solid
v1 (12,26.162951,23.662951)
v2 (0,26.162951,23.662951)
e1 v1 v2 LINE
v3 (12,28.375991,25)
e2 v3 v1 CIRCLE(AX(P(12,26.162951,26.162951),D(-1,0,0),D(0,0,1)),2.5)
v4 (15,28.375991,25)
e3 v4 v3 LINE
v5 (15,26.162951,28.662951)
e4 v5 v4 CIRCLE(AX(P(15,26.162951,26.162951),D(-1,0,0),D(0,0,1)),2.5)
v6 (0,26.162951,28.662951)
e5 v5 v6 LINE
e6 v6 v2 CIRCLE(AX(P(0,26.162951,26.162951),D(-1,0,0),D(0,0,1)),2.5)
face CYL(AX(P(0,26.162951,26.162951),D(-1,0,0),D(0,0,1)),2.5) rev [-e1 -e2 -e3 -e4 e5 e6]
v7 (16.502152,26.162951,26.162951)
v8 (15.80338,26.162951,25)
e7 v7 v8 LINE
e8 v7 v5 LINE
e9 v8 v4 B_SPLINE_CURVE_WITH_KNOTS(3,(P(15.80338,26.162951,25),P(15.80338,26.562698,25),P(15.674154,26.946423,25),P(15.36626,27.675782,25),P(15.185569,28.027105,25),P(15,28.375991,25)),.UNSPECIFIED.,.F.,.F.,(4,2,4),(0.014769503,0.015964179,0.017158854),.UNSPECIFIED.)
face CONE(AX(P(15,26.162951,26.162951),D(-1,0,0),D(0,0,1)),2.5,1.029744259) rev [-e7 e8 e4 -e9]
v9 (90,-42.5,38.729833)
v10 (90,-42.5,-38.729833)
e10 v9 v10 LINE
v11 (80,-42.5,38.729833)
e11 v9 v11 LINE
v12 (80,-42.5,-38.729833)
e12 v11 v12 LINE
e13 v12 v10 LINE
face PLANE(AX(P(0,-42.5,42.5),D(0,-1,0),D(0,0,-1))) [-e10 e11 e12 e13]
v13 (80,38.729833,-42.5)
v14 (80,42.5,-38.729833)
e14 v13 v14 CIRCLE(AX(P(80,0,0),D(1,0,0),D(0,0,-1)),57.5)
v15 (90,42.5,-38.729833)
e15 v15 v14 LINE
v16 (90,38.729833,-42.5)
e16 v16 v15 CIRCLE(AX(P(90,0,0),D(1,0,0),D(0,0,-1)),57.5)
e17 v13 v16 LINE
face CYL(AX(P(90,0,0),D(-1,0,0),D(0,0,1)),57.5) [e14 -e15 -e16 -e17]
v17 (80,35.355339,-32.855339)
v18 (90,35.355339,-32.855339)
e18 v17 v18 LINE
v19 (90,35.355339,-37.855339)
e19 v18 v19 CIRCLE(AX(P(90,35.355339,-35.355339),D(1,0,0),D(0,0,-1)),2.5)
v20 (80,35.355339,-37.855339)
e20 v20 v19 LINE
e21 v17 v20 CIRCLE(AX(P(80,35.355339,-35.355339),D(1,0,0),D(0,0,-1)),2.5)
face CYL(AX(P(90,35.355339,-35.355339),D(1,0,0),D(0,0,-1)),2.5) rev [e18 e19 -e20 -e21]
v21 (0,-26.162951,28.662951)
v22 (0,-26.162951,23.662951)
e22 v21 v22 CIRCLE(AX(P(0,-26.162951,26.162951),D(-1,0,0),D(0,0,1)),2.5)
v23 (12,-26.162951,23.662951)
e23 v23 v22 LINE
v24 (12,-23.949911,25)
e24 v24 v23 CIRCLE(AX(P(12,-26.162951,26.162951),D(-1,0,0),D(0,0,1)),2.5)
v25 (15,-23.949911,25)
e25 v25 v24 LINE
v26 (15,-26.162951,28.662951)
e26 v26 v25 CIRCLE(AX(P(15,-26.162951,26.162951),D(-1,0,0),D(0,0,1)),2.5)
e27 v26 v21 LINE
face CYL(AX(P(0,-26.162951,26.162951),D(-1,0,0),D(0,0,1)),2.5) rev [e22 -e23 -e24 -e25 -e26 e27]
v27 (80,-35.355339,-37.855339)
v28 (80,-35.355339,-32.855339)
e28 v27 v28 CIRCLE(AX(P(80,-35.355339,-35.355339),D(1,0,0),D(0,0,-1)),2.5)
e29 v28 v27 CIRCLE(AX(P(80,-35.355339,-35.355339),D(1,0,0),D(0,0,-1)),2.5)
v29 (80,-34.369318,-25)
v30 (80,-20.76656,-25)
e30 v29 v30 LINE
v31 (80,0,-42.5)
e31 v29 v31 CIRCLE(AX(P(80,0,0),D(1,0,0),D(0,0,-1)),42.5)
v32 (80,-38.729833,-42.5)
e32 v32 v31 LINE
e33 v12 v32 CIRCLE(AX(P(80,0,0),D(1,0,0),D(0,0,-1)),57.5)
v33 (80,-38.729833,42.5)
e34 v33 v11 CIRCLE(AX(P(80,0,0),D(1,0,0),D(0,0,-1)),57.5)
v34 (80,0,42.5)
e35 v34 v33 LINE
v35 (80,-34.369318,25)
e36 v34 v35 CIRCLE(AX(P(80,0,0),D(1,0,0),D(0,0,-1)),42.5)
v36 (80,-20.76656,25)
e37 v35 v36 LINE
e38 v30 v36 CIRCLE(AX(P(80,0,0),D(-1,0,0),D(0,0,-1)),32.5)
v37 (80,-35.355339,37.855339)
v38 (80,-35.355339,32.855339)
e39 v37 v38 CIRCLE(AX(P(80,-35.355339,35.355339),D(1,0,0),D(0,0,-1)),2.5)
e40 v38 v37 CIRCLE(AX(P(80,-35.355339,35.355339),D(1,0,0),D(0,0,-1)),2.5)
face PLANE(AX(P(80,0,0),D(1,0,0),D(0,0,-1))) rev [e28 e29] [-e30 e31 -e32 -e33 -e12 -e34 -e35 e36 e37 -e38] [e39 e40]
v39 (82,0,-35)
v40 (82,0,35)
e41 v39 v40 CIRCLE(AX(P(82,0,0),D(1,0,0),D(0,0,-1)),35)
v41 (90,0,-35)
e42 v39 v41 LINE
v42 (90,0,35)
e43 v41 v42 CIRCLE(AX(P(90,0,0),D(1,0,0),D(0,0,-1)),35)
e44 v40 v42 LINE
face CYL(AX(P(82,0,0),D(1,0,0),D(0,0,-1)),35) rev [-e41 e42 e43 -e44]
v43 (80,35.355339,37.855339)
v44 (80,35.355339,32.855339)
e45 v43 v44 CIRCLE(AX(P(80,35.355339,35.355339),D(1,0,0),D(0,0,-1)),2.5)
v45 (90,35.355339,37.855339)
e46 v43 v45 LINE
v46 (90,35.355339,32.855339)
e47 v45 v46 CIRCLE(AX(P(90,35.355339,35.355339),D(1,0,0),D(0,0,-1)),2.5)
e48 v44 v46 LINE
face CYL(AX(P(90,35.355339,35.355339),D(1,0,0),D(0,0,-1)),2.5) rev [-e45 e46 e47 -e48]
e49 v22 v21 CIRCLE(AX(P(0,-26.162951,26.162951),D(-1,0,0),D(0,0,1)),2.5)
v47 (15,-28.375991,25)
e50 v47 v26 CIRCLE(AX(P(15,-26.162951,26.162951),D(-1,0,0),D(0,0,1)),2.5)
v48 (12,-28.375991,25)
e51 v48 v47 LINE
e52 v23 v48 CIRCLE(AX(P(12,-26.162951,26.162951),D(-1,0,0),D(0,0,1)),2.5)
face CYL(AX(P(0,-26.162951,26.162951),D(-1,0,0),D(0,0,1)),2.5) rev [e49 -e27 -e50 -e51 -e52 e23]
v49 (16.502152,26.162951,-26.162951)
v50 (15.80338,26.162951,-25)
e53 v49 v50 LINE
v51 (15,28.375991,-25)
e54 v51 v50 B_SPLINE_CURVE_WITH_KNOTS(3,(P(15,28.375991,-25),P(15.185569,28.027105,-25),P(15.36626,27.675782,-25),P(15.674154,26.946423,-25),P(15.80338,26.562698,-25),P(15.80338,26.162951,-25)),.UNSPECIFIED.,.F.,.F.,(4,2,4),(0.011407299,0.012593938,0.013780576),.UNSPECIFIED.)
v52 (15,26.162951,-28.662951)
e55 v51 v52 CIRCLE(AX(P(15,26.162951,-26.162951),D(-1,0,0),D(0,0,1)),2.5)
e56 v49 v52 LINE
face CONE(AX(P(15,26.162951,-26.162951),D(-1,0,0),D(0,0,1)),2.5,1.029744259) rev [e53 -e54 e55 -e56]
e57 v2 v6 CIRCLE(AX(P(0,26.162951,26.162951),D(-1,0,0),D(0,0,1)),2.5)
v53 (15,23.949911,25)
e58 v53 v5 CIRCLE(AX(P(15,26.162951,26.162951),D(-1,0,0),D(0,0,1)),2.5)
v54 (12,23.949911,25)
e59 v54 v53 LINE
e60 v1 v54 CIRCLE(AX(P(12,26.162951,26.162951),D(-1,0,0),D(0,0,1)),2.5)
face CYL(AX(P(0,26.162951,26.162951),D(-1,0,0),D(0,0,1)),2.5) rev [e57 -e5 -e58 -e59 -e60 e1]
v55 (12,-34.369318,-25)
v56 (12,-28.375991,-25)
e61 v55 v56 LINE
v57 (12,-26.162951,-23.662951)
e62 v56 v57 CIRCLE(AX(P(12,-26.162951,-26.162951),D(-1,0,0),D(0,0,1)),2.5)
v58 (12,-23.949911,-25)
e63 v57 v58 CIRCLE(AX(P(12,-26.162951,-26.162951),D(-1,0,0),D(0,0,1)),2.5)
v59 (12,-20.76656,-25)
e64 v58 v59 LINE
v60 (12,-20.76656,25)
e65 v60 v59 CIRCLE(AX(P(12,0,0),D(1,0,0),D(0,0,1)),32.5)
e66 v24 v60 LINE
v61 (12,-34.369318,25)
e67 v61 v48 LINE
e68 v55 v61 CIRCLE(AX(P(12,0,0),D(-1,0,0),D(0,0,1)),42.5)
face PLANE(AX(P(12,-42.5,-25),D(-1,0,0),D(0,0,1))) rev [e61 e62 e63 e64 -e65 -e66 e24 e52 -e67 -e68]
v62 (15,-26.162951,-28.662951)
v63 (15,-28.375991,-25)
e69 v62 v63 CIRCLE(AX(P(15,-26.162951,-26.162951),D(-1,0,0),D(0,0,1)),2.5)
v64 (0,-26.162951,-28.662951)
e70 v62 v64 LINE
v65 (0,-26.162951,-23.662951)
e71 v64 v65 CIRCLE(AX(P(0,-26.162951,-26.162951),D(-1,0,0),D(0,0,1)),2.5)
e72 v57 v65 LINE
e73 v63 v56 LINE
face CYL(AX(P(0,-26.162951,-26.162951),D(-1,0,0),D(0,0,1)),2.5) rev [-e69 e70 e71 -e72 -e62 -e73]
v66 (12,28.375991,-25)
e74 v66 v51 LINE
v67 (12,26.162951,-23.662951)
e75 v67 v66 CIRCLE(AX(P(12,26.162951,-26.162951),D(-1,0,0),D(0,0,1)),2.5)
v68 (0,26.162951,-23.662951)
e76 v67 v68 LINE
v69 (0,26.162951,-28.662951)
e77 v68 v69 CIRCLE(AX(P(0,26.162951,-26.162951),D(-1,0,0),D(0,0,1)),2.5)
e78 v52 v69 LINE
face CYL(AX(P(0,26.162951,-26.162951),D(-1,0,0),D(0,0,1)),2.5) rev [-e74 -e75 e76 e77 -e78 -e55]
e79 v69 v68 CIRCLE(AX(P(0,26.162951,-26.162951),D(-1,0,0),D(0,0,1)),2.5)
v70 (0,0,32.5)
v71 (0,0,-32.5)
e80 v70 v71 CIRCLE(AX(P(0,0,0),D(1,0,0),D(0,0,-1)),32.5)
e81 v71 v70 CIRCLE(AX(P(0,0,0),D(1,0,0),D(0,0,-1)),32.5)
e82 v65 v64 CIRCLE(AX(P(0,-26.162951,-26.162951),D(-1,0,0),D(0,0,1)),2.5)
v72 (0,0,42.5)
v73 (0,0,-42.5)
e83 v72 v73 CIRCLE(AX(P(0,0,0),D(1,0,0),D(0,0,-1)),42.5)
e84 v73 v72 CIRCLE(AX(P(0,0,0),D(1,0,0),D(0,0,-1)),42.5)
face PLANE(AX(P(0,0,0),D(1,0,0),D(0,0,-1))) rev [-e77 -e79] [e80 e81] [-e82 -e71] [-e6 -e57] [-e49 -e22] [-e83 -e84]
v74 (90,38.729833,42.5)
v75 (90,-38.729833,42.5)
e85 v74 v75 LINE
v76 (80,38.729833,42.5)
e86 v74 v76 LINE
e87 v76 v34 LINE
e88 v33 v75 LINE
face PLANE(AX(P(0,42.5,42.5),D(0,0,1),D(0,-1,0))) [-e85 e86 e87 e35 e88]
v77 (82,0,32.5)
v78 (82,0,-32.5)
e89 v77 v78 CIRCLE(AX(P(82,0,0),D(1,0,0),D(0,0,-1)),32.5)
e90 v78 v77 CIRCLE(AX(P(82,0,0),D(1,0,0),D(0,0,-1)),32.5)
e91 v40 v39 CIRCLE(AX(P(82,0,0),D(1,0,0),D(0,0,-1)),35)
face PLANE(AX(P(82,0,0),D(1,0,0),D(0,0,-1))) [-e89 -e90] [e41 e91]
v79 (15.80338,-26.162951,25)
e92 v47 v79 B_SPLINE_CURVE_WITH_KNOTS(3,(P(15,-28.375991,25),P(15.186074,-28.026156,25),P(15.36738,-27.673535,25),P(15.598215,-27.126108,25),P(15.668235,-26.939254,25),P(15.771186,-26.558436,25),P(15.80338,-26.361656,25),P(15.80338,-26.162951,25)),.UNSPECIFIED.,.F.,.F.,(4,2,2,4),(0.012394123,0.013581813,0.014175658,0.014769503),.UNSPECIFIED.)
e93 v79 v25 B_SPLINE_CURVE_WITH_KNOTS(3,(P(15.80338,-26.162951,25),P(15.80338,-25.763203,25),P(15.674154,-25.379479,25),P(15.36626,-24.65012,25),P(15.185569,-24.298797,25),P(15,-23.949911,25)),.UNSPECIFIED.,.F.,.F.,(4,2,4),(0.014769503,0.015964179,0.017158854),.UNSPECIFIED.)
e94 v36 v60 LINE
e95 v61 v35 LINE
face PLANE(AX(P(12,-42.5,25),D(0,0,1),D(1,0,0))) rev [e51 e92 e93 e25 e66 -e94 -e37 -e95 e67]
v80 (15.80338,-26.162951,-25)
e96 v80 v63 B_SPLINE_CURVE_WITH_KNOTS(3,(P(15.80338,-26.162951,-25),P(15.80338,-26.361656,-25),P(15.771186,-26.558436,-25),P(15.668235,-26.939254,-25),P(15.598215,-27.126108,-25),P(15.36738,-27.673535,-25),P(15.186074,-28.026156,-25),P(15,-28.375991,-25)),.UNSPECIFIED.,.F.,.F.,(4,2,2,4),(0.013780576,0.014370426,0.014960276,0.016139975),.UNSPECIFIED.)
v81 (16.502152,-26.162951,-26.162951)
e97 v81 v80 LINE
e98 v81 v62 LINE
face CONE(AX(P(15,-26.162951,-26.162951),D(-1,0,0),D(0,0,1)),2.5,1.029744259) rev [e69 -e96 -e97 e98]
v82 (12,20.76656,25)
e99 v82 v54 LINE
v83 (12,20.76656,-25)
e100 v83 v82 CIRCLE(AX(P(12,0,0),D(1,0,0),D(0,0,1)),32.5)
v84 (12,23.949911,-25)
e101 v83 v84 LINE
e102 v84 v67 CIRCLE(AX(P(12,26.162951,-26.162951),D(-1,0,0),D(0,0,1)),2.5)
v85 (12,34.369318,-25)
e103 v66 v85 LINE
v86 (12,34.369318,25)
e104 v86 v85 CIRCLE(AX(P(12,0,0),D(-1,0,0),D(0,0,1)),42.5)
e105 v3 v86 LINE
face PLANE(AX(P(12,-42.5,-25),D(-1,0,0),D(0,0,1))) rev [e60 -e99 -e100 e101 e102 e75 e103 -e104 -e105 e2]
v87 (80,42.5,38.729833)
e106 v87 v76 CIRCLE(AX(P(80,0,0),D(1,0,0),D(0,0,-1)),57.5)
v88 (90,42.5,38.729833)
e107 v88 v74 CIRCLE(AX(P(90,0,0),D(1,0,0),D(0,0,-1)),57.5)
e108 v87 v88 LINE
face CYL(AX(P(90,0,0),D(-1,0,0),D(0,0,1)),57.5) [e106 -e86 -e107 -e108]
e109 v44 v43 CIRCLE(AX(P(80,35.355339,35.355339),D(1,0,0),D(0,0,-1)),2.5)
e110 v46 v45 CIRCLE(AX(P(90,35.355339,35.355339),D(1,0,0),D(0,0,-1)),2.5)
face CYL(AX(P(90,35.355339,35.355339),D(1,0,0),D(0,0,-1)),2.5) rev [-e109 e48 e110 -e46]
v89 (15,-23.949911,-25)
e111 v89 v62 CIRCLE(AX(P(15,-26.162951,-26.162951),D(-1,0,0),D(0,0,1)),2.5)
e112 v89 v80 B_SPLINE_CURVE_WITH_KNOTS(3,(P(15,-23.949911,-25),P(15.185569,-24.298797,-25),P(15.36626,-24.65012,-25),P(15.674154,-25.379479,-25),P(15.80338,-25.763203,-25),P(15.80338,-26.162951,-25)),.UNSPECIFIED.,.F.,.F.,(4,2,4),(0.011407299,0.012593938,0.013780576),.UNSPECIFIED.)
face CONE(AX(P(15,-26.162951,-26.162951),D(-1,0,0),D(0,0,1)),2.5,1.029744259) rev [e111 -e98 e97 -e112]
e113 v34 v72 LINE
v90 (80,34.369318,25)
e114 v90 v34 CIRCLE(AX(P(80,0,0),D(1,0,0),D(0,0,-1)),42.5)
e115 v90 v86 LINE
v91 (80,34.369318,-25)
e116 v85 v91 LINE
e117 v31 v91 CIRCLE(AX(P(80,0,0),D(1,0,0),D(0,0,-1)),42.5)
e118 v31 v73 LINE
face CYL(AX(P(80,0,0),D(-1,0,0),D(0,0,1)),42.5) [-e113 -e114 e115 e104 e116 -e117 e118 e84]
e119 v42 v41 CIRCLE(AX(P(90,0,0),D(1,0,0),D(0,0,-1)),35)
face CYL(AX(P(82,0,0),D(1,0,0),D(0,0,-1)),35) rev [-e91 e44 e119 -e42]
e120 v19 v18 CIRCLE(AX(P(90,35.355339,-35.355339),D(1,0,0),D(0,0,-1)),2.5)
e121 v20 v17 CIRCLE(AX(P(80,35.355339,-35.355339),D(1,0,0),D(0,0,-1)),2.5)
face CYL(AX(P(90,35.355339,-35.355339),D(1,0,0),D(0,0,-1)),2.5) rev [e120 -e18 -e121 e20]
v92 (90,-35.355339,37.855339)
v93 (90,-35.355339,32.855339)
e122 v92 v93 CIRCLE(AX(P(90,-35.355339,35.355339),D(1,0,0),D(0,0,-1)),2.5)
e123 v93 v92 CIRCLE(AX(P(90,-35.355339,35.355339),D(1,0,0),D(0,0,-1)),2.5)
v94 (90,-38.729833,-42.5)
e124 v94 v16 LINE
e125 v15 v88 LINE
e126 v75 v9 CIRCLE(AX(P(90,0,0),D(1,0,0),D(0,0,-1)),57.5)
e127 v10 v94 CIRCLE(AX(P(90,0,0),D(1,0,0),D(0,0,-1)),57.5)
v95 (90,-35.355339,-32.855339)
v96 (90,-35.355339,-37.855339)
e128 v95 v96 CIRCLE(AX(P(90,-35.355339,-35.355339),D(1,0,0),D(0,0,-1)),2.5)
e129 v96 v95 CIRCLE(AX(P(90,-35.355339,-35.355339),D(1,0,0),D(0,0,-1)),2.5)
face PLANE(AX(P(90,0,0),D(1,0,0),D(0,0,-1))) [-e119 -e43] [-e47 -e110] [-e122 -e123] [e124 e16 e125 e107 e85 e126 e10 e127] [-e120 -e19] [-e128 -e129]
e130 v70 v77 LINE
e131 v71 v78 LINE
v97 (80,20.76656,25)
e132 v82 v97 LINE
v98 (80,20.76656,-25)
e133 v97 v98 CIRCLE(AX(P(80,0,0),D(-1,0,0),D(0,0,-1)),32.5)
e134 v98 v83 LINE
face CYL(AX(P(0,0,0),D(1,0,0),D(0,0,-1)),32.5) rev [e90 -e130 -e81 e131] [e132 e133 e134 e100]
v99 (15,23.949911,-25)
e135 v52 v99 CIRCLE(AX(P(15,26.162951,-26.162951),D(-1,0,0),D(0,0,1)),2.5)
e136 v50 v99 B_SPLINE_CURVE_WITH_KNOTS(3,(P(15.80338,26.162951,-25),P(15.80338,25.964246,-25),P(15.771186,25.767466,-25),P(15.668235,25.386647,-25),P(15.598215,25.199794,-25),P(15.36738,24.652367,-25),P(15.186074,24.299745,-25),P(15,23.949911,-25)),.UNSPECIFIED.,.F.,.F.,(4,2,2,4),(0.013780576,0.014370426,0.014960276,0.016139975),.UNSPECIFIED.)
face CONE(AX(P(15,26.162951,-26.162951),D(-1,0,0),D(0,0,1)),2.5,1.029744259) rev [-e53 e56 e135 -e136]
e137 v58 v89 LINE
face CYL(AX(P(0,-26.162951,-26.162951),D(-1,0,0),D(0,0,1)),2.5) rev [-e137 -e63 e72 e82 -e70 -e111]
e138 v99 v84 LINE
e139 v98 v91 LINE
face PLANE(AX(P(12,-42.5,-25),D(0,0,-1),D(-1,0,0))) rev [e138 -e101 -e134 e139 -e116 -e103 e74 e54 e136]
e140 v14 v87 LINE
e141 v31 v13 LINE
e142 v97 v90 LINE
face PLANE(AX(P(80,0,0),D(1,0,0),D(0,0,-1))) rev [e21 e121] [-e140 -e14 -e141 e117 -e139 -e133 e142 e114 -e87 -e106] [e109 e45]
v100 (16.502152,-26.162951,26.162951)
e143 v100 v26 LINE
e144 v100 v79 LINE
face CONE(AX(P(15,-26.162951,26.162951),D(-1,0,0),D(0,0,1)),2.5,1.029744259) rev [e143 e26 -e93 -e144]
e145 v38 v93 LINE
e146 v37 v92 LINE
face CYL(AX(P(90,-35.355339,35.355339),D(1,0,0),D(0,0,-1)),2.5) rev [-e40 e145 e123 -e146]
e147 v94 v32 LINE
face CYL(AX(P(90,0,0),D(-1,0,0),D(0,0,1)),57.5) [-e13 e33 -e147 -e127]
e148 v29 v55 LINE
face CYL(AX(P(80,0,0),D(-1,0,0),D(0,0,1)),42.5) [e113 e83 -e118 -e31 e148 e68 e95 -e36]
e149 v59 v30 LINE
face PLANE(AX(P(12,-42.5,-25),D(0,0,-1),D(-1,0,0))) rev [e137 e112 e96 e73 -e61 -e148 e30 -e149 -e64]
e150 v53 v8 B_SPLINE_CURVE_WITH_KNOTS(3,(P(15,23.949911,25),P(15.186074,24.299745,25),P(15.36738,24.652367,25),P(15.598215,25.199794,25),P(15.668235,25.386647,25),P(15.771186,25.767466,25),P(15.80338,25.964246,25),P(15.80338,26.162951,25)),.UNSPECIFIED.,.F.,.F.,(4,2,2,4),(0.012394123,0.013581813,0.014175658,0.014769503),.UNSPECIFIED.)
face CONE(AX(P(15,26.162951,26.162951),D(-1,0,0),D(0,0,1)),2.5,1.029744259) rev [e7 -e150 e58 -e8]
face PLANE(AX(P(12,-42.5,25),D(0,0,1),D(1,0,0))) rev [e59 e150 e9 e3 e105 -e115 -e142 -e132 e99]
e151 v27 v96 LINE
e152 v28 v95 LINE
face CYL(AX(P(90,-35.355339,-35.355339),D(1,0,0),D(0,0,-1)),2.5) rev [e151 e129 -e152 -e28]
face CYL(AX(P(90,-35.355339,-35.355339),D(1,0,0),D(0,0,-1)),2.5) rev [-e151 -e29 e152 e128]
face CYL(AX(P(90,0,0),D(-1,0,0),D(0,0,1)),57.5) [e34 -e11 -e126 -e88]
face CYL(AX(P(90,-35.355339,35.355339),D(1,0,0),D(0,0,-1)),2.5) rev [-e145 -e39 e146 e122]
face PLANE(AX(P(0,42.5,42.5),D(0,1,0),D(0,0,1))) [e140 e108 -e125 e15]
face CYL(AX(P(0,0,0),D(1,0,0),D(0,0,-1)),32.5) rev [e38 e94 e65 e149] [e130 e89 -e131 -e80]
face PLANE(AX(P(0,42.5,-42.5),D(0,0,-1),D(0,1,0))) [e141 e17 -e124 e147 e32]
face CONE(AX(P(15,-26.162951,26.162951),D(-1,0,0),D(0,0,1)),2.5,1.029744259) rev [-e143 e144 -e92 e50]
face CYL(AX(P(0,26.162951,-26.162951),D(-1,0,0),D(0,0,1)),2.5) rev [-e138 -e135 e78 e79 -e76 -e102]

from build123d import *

# Parameters (mm, degrees)
SKETCH_1_R               = 42.5
EXTRUDE_1_DEPTH          = 80
SKETCH_2_R               = 57.5
EXTRUDE_2_DEPTH          = 10
SKETCH_3_OUTSIDE_W       = 154.176
SKETCH_3_OUTSIDE_H       = 154.176
SKETCH_3_OUTSIDE_W_2     = 85
SKETCH_3_OUTSIDE_H_2     = 85
CUT_EXTRUDE_1_DEPTH      = 122.295094707
SKETCH_4_R               = 35
CUT_EXTRUDE_2_DEPTH      = 8
PATTERN_CIRCULAR_1_COUNT = 4
SKETCH_7_R               = 32.5
CUT_EXTRUDE_3_DEPTH      = 102.668579217
CUT_EXTRUDE_4_DEPTH      = 109.22430411
CUT_EXTRUDE_4_DEPTH_BACK = 109.22430411
SKETCH_8_W               = 68
SKETCH_8_H               = 50
PATTERN_CIRCULAR_2_COUNT = 4


with BuildPart() as part:
    # 草图1 → 凸台-拉伸1 (new body)
    with BuildSketch(Plane(origin=(0, 0, 0), x_dir=(0, 0, -1), z_dir=(1, 0, 0))):
        Circle(SKETCH_1_R)
    extrude(amount=EXTRUDE_1_DEPTH)

    # 草图2 → 凸台-拉伸2 (add)
    with BuildSketch(Plane(origin=(80, 0, 0), x_dir=(0, 0, -1), z_dir=(1, 0, 0))):
        Circle(SKETCH_2_R)
    extrude(amount=EXTRUDE_2_DEPTH)

    # 草图3 outside → 切除-拉伸1 (cut, through all)
    with BuildSketch(Plane(origin=(90, 0, 0), x_dir=(0, 0, -1), z_dir=(1, 0, 0))):
        Rectangle(SKETCH_3_OUTSIDE_W, SKETCH_3_OUTSIDE_H)
        Rectangle(SKETCH_3_OUTSIDE_W_2, SKETCH_3_OUTSIDE_H_2, mode=Mode.SUBTRACT)
    extrude(amount=-CUT_EXTRUDE_1_DEPTH, mode=Mode.SUBTRACT)

    # 草图4 → 切除-拉伸2 (cut)
    with BuildSketch(Plane(origin=(90, 0, 0), x_dir=(0, 0, -1), z_dir=(1, 0, 0))):
        Circle(SKETCH_4_R)
    extrude(amount=-CUT_EXTRUDE_2_DEPTH, mode=Mode.SUBTRACT)

    # 草图6 → M6 螺纹孔1 (revolve, cut)
    with BuildSketch(Plane(origin=(90, 35.355339059, 35.355339059), x_dir=(0, 0, -1), z_dir=(0, 1, 0))):
        Polygon((0, 0), (0, 16.502151548), (2.5, 15), (2.5, 0), align=None)
    hole_wizard_m6_1 = revolve(axis=Axis((96.35, 35.355339059, 35.355339059), (-1, 0, 0)), mode=Mode.SUBTRACT)

    # 阵列(圆周)1: M6 螺纹孔1 ×4 about axis
    pattern_circular_1_axis = Axis((0, 0, 0), (1, 0, 0))
    for i in range(1, PATTERN_CIRCULAR_1_COUNT):
        add(hole_wizard_m6_1.rotate(pattern_circular_1_axis, i * 360 / PATTERN_CIRCULAR_1_COUNT), mode=Mode.SUBTRACT)

    # 草图7 → 切除-拉伸3 (cut, through all)
    with BuildSketch(Plane(origin=(82, 0, 0), x_dir=(0, 0, -1), z_dir=(1, 0, 0))):
        Circle(SKETCH_7_R)
    extrude(amount=-CUT_EXTRUDE_3_DEPTH, mode=Mode.SUBTRACT)

    # 草图8 → 切除-拉伸4 (cut, two sides: drawn at the far end of the back side and taken through both)
    with BuildSketch(Plane(origin=(0, 0, 0), x_dir=(1, 0, 0), z_dir=(0, 1, 0)).offset(-CUT_EXTRUDE_4_DEPTH_BACK)):
        with Locations((46, 0)):
            Rectangle(SKETCH_8_W, SKETCH_8_H)
    extrude(amount=CUT_EXTRUDE_4_DEPTH + CUT_EXTRUDE_4_DEPTH_BACK, mode=Mode.SUBTRACT)

    # 草图10 → M6 螺纹孔2 (revolve, cut)
    with BuildSketch(Plane(origin=(0, 26.162950904, -26.162950904), x_dir=(0, 0, 1), z_dir=(0, 1, 0))):
        Polygon((0, 0), (0, 16.502151548), (2.5, 15), (2.5, 0), align=None)
    hole_wizard_m6_2 = revolve(axis=Axis((-6.35, 26.162950904, -26.162950904), (1, 0, 0)), mode=Mode.SUBTRACT)

    # 阵列(圆周)2: M6 螺纹孔2 ×4 about axis
    pattern_circular_2_axis = Axis((0, 0, 0), (1, 0, 0))
    for i in range(1, PATTERN_CIRCULAR_2_COUNT):
        add(hole_wizard_m6_2.rotate(pattern_circular_2_axis, i * 360 / PATTERN_CIRCULAR_2_COUNT), mode=Mode.SUBTRACT)


solid = part.part
